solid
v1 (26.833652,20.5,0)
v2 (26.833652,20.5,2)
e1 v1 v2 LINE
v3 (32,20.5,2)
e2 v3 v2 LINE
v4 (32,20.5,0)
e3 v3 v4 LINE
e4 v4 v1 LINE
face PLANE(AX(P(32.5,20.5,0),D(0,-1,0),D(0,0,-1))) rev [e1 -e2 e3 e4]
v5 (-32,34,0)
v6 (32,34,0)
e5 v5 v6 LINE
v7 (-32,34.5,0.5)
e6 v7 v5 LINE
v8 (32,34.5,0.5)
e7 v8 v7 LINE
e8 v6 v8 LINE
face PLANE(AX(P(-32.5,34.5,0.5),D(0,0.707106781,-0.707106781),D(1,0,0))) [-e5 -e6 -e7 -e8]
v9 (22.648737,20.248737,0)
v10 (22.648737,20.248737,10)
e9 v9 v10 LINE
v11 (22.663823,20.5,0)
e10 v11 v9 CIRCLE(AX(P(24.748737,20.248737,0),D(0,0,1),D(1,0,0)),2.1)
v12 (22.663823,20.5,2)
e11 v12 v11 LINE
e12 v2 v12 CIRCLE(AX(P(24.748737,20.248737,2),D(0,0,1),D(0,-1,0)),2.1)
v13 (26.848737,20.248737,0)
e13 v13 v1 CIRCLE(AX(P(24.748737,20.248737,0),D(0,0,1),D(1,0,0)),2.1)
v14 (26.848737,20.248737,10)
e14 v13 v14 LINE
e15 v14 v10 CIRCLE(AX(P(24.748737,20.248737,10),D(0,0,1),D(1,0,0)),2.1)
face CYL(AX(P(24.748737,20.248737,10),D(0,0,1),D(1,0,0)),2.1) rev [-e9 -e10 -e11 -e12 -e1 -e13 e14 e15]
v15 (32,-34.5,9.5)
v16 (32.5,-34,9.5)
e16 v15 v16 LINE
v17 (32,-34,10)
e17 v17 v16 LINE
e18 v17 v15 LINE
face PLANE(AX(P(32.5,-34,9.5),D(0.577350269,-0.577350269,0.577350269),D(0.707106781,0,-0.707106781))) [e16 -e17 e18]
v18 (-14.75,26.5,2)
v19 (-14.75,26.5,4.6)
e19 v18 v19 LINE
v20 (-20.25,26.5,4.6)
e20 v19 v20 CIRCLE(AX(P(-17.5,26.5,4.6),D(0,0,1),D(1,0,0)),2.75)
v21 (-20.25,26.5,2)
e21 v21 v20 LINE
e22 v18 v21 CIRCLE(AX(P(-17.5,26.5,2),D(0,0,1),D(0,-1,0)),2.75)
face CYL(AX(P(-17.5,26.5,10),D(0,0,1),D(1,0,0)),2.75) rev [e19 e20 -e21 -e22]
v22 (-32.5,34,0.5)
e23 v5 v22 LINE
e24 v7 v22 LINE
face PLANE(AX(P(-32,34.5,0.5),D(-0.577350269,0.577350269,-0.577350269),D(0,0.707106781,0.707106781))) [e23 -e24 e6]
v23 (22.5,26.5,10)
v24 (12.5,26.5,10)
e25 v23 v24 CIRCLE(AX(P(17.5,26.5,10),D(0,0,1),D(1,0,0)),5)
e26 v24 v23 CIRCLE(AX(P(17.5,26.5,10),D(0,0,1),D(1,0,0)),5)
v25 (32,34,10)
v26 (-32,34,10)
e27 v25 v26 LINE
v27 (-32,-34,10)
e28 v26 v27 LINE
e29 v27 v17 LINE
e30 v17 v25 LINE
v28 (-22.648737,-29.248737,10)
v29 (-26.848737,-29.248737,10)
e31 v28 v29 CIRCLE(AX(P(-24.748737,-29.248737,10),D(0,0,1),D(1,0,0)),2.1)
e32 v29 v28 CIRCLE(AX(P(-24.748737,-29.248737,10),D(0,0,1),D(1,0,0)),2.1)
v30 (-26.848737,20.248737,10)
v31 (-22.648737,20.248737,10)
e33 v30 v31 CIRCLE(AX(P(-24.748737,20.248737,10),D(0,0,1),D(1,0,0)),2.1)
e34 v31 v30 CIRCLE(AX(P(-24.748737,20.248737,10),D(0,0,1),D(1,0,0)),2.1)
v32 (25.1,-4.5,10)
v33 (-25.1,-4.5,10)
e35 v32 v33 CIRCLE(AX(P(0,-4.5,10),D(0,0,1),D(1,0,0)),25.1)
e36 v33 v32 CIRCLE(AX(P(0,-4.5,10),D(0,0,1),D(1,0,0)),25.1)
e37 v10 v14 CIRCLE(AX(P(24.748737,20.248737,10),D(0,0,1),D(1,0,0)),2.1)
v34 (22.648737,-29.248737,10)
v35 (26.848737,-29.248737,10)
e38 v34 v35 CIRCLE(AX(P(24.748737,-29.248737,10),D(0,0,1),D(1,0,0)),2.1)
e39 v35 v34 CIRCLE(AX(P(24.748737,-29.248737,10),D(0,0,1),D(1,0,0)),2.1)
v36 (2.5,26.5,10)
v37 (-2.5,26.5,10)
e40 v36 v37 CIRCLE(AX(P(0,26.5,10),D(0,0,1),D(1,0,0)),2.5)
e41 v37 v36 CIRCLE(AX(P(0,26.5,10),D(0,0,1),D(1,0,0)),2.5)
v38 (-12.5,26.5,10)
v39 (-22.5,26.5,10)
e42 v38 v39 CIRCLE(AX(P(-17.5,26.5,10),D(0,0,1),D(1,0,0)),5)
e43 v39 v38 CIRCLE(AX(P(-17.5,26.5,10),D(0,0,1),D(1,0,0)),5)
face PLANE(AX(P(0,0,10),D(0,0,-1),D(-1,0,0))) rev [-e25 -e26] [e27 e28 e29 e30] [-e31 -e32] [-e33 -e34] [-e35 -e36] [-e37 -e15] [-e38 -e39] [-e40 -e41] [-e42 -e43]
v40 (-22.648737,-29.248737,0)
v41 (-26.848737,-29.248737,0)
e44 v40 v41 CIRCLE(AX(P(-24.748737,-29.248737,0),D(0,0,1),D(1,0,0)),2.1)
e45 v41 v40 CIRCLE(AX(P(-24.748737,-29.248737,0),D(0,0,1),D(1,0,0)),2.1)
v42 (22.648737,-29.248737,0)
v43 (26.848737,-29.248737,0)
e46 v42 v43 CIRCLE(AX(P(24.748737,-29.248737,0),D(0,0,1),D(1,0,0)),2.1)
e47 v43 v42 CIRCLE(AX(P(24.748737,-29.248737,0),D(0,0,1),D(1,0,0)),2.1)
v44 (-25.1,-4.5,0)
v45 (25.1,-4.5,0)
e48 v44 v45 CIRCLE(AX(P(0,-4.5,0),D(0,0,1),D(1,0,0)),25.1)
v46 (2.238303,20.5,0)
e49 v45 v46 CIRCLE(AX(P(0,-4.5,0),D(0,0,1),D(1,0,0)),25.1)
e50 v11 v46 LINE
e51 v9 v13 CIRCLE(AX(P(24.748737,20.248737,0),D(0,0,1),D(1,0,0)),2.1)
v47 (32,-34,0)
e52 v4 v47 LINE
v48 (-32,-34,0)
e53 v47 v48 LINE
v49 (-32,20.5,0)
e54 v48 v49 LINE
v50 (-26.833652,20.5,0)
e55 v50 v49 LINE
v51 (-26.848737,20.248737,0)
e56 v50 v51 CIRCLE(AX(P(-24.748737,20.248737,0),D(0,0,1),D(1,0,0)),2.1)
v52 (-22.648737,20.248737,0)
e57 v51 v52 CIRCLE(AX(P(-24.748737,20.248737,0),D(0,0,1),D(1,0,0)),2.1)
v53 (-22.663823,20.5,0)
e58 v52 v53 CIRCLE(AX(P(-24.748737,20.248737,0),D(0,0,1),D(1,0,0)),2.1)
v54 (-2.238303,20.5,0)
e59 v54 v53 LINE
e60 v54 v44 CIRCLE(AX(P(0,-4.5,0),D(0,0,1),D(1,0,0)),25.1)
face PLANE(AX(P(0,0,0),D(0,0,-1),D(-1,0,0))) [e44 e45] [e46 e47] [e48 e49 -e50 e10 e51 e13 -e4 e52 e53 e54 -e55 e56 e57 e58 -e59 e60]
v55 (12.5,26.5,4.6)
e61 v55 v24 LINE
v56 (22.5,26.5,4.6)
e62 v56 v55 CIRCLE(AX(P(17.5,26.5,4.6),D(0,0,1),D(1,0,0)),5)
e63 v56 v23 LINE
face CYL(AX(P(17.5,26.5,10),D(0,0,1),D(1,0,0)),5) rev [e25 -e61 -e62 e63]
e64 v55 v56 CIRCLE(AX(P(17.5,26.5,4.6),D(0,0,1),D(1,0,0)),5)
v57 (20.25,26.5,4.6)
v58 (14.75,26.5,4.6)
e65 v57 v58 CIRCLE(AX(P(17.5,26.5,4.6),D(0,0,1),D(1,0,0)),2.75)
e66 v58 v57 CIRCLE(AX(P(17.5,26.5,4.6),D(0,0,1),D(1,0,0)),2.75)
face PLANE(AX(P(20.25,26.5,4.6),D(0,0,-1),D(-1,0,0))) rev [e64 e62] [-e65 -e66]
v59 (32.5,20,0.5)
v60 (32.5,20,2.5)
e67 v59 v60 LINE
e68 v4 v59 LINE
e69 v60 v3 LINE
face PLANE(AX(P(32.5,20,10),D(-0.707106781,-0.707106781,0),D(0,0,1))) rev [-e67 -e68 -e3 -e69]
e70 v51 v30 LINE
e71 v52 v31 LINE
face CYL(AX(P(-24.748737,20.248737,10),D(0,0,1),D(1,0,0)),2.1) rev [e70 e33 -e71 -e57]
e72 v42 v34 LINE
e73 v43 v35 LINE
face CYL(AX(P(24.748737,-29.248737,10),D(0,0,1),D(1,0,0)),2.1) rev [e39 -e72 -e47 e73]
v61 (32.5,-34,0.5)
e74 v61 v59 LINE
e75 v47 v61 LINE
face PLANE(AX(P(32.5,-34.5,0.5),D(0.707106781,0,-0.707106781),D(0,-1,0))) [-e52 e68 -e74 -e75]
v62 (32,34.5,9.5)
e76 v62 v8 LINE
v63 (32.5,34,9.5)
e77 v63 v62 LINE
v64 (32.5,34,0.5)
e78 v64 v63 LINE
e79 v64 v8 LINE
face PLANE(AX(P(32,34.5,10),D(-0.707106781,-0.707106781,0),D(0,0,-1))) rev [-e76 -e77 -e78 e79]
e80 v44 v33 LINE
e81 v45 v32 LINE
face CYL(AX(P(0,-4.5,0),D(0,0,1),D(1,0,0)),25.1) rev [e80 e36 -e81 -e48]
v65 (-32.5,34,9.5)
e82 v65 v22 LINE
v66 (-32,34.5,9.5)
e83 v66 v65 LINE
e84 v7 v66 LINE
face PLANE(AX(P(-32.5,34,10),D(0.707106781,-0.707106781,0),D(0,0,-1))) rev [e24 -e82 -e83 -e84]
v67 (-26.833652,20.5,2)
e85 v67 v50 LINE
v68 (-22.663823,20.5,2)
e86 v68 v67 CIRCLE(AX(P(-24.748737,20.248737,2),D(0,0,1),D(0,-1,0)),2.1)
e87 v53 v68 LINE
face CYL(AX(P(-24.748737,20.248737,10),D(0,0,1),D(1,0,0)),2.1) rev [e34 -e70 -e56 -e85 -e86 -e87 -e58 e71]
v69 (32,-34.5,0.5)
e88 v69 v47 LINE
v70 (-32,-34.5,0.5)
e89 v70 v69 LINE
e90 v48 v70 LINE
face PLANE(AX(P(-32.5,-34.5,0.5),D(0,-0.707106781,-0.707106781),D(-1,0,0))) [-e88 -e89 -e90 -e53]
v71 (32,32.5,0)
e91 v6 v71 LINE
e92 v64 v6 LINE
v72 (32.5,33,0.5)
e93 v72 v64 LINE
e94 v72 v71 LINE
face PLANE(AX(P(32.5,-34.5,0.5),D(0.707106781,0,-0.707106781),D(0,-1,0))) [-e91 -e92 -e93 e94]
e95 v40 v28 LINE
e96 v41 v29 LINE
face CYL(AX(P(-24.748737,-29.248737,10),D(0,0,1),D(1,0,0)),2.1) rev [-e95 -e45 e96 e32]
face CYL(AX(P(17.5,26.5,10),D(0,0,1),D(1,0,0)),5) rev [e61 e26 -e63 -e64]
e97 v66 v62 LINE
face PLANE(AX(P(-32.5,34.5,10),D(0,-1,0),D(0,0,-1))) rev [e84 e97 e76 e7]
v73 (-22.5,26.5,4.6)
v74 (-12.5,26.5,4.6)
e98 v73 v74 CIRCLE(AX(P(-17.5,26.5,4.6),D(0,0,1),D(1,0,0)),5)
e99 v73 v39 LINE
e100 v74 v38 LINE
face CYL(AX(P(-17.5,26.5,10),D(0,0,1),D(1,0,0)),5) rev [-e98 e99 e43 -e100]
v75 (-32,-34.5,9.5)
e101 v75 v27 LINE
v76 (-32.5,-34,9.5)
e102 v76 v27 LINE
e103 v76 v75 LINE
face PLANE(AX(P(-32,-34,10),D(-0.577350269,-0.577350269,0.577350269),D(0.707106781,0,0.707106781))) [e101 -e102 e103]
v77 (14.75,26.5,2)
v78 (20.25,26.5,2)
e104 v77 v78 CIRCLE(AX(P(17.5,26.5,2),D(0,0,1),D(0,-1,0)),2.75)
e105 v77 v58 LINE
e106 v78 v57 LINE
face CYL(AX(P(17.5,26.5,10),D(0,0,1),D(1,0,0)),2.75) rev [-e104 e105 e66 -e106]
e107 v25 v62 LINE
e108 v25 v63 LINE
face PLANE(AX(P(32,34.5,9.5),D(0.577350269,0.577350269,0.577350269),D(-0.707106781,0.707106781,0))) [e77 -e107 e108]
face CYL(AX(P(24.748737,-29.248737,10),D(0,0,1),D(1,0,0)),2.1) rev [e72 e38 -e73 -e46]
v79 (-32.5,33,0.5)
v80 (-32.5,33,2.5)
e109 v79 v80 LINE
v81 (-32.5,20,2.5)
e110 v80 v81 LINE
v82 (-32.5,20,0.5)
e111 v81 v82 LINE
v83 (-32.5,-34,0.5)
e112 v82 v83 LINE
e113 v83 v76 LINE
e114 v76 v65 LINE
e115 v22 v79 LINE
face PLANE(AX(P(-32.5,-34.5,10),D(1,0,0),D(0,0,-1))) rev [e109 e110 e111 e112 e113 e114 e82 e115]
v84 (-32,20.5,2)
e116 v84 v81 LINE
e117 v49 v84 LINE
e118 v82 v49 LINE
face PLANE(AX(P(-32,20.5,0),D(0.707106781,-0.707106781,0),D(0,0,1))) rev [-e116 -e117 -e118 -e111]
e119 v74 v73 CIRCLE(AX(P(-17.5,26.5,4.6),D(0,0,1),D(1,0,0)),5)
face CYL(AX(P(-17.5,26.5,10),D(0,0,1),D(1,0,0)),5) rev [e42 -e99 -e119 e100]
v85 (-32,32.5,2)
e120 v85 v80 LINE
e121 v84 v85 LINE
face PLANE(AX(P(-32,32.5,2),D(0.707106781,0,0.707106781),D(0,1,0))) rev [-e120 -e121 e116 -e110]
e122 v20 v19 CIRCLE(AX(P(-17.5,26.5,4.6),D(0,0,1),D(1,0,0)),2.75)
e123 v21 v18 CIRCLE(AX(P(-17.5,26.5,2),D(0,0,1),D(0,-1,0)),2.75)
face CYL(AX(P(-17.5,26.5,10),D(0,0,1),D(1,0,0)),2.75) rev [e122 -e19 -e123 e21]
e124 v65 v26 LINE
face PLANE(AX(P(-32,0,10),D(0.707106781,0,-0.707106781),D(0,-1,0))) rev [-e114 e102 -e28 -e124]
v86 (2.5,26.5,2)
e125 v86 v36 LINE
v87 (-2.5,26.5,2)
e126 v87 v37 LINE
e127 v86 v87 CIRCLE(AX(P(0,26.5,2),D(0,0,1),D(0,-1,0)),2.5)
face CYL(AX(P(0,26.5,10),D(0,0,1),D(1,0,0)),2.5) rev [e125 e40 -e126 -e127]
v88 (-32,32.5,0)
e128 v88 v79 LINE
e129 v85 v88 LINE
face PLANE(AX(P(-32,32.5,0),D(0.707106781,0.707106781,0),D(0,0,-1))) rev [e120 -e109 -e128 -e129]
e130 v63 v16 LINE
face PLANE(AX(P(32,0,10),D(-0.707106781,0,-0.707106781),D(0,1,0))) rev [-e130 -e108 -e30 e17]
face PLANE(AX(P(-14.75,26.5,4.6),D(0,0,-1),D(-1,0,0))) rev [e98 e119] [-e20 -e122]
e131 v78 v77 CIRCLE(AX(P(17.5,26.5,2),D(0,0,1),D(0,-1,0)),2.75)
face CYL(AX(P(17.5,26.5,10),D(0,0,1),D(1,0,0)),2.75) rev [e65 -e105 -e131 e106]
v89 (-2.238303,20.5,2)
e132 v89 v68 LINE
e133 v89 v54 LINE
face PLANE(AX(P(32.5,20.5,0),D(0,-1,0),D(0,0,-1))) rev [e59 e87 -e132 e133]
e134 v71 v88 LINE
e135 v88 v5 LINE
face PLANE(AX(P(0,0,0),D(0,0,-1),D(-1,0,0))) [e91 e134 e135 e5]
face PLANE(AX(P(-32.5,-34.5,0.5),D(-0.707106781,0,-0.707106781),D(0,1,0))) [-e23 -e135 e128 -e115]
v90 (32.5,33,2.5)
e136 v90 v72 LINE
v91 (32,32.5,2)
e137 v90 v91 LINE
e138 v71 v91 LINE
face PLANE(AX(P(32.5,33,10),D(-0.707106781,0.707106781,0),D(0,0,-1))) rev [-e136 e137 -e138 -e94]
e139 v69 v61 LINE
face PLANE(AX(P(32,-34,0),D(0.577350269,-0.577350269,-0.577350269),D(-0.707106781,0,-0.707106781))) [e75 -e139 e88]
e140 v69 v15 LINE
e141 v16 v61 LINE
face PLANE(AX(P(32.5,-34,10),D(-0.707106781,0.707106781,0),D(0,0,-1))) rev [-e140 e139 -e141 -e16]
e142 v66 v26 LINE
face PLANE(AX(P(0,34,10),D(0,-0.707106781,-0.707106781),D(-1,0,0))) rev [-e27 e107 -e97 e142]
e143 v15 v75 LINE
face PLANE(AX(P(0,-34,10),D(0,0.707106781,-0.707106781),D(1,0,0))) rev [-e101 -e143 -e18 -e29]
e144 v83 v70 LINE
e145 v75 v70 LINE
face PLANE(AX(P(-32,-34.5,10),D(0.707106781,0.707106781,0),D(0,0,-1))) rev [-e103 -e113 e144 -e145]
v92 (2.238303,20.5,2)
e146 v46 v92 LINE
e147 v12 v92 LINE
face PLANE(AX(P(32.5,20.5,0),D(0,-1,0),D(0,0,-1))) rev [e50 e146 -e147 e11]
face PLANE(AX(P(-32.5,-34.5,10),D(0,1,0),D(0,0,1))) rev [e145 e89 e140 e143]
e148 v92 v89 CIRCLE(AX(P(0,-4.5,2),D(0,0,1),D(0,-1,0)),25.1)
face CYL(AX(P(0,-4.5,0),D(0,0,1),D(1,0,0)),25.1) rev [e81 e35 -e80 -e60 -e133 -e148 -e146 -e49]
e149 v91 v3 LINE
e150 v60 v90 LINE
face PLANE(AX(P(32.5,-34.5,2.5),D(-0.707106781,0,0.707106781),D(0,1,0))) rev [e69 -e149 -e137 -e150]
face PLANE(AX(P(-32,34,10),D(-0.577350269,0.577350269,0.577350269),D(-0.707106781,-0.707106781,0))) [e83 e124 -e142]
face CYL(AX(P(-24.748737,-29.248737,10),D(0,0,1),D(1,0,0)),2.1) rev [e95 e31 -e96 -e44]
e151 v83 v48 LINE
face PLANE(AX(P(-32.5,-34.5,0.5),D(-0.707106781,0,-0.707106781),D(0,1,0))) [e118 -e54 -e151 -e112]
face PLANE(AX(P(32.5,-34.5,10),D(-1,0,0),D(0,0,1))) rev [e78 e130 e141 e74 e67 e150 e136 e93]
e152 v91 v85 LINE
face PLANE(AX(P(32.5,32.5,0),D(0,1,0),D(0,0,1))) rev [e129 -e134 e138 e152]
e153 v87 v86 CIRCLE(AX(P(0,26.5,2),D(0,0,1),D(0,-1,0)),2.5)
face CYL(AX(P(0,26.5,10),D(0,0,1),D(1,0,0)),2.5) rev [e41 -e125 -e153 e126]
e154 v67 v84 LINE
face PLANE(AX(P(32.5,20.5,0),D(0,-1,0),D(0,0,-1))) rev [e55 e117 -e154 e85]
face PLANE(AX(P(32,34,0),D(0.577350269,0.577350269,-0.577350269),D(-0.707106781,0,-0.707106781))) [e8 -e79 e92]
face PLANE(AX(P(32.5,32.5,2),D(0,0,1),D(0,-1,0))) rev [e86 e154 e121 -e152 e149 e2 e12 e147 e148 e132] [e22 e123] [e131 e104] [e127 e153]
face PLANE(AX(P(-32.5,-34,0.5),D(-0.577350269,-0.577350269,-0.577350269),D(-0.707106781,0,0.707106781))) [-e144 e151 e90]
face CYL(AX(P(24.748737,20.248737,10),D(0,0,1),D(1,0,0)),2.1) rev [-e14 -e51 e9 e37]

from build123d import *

# Parameters (mm, degrees)
SKETCH_1_W                     = 65
SKETCH_1_H                     = 69
EXTRUDE_1_DEPTH                = 10
SKETCH_2_W                     = 2
SKETCH_2_H                     = 12
CUT_EXTRUDE_1_DEPTH            = 75.264729179
SKETCH_3_R                     = 25.1
CUT_EXTRUDE_2_DEPTH            = 49.440685379
HOLE_WIZARD_M5_1_D             = 4.2
HOLE_WIZARD_M5_1_2_D           = 5.5
HOLE_WIZARD_M5_1_2_CBORE_D     = 10
HOLE_WIZARD_M5_1_2_CBORE_DEPTH = 5.4
MM_1_D                         = 5
CHAMFER_1_SIZE                 = 0.5


with BuildPart() as part:
    # 草图1 → 凸台-拉伸1 (new body)
    with BuildSketch(Plane.XY):
        Rectangle(SKETCH_1_W, SKETCH_1_H)
    extrude(amount=EXTRUDE_1_DEPTH)

    # 草图2 → 切除-拉伸1 (cut, through all)
    with BuildSketch(Plane.ZY.offset(32.5)):
        with Locations((1, 26.5)):
            Rectangle(SKETCH_2_W, SKETCH_2_H)
    extrude(amount=-CUT_EXTRUDE_1_DEPTH, mode=Mode.SUBTRACT)

    # 草图3 → 切除-拉伸2 (cut, through all)
    with BuildSketch(Plane.XY.offset(10)):
        with Locations((0, -4.5)):
            Circle(SKETCH_3_R)
    extrude(amount=-CUT_EXTRUDE_2_DEPTH, mode=Mode.SUBTRACT)

    # Hole Wizard M5 _1 (through all)
    with Locations(Plane.XY.offset(10)):
        with Locations((24.748737342, 20.248737342), (24.748737342, -29.248737342), (-24.748737342, -29.248737342), (-24.748737342, 20.248737342)):
            Hole(HOLE_WIZARD_M5_1_D / 2)

    # Hole Wizard M5 _1 2 (through all)
    with Locations(Plane.XY.offset(10)):
        with Locations((17.5, 26.5), (-17.5, 26.5)):
            CounterBoreHole(HOLE_WIZARD_M5_1_2_D / 2, HOLE_WIZARD_M5_1_2_CBORE_D / 2, HOLE_WIZARD_M5_1_2_CBORE_DEPTH)

    # 大小mm 暗销孔1 (through all)
    with Locations(Plane.XY.offset(10)):
        with Locations((0, 26.5)):
            Hole(MM_1_D / 2)

    # 倒角1
    chamfer_1_edges = [part.edges().sort_by_distance(p)[0] for p in [
        (-32.5, 0, 10),
        (32.5, 33.5, 0),
        (-32.5, -7, 0),
        (0, -34.5, 10),
        (32.5, 32.5, 1),
        (32.5, 26.5, 2),
        (32.5, 20.5, 1),
        (-32.5, 20.5, 1),
        (-32.5, 26.5, 2),
        (-32.5, 32.5, 1),
        (32.5, 0, 10),
        (0, -34.5, 0),
        (-32.5, 33.5, 0),
        (0, 34.5, 0),
        (32.5, -7, 0),
        (32.5, -34.5, 5),
        (-32.5, -34.5, 5),
        (-32.5, 34.5, 5),
        (32.5, 34.5, 5),
        (0, 34.5, 10),
    ]]
    chamfer(chamfer_1_edges, length=CHAMFER_1_SIZE)


solid = part.part
